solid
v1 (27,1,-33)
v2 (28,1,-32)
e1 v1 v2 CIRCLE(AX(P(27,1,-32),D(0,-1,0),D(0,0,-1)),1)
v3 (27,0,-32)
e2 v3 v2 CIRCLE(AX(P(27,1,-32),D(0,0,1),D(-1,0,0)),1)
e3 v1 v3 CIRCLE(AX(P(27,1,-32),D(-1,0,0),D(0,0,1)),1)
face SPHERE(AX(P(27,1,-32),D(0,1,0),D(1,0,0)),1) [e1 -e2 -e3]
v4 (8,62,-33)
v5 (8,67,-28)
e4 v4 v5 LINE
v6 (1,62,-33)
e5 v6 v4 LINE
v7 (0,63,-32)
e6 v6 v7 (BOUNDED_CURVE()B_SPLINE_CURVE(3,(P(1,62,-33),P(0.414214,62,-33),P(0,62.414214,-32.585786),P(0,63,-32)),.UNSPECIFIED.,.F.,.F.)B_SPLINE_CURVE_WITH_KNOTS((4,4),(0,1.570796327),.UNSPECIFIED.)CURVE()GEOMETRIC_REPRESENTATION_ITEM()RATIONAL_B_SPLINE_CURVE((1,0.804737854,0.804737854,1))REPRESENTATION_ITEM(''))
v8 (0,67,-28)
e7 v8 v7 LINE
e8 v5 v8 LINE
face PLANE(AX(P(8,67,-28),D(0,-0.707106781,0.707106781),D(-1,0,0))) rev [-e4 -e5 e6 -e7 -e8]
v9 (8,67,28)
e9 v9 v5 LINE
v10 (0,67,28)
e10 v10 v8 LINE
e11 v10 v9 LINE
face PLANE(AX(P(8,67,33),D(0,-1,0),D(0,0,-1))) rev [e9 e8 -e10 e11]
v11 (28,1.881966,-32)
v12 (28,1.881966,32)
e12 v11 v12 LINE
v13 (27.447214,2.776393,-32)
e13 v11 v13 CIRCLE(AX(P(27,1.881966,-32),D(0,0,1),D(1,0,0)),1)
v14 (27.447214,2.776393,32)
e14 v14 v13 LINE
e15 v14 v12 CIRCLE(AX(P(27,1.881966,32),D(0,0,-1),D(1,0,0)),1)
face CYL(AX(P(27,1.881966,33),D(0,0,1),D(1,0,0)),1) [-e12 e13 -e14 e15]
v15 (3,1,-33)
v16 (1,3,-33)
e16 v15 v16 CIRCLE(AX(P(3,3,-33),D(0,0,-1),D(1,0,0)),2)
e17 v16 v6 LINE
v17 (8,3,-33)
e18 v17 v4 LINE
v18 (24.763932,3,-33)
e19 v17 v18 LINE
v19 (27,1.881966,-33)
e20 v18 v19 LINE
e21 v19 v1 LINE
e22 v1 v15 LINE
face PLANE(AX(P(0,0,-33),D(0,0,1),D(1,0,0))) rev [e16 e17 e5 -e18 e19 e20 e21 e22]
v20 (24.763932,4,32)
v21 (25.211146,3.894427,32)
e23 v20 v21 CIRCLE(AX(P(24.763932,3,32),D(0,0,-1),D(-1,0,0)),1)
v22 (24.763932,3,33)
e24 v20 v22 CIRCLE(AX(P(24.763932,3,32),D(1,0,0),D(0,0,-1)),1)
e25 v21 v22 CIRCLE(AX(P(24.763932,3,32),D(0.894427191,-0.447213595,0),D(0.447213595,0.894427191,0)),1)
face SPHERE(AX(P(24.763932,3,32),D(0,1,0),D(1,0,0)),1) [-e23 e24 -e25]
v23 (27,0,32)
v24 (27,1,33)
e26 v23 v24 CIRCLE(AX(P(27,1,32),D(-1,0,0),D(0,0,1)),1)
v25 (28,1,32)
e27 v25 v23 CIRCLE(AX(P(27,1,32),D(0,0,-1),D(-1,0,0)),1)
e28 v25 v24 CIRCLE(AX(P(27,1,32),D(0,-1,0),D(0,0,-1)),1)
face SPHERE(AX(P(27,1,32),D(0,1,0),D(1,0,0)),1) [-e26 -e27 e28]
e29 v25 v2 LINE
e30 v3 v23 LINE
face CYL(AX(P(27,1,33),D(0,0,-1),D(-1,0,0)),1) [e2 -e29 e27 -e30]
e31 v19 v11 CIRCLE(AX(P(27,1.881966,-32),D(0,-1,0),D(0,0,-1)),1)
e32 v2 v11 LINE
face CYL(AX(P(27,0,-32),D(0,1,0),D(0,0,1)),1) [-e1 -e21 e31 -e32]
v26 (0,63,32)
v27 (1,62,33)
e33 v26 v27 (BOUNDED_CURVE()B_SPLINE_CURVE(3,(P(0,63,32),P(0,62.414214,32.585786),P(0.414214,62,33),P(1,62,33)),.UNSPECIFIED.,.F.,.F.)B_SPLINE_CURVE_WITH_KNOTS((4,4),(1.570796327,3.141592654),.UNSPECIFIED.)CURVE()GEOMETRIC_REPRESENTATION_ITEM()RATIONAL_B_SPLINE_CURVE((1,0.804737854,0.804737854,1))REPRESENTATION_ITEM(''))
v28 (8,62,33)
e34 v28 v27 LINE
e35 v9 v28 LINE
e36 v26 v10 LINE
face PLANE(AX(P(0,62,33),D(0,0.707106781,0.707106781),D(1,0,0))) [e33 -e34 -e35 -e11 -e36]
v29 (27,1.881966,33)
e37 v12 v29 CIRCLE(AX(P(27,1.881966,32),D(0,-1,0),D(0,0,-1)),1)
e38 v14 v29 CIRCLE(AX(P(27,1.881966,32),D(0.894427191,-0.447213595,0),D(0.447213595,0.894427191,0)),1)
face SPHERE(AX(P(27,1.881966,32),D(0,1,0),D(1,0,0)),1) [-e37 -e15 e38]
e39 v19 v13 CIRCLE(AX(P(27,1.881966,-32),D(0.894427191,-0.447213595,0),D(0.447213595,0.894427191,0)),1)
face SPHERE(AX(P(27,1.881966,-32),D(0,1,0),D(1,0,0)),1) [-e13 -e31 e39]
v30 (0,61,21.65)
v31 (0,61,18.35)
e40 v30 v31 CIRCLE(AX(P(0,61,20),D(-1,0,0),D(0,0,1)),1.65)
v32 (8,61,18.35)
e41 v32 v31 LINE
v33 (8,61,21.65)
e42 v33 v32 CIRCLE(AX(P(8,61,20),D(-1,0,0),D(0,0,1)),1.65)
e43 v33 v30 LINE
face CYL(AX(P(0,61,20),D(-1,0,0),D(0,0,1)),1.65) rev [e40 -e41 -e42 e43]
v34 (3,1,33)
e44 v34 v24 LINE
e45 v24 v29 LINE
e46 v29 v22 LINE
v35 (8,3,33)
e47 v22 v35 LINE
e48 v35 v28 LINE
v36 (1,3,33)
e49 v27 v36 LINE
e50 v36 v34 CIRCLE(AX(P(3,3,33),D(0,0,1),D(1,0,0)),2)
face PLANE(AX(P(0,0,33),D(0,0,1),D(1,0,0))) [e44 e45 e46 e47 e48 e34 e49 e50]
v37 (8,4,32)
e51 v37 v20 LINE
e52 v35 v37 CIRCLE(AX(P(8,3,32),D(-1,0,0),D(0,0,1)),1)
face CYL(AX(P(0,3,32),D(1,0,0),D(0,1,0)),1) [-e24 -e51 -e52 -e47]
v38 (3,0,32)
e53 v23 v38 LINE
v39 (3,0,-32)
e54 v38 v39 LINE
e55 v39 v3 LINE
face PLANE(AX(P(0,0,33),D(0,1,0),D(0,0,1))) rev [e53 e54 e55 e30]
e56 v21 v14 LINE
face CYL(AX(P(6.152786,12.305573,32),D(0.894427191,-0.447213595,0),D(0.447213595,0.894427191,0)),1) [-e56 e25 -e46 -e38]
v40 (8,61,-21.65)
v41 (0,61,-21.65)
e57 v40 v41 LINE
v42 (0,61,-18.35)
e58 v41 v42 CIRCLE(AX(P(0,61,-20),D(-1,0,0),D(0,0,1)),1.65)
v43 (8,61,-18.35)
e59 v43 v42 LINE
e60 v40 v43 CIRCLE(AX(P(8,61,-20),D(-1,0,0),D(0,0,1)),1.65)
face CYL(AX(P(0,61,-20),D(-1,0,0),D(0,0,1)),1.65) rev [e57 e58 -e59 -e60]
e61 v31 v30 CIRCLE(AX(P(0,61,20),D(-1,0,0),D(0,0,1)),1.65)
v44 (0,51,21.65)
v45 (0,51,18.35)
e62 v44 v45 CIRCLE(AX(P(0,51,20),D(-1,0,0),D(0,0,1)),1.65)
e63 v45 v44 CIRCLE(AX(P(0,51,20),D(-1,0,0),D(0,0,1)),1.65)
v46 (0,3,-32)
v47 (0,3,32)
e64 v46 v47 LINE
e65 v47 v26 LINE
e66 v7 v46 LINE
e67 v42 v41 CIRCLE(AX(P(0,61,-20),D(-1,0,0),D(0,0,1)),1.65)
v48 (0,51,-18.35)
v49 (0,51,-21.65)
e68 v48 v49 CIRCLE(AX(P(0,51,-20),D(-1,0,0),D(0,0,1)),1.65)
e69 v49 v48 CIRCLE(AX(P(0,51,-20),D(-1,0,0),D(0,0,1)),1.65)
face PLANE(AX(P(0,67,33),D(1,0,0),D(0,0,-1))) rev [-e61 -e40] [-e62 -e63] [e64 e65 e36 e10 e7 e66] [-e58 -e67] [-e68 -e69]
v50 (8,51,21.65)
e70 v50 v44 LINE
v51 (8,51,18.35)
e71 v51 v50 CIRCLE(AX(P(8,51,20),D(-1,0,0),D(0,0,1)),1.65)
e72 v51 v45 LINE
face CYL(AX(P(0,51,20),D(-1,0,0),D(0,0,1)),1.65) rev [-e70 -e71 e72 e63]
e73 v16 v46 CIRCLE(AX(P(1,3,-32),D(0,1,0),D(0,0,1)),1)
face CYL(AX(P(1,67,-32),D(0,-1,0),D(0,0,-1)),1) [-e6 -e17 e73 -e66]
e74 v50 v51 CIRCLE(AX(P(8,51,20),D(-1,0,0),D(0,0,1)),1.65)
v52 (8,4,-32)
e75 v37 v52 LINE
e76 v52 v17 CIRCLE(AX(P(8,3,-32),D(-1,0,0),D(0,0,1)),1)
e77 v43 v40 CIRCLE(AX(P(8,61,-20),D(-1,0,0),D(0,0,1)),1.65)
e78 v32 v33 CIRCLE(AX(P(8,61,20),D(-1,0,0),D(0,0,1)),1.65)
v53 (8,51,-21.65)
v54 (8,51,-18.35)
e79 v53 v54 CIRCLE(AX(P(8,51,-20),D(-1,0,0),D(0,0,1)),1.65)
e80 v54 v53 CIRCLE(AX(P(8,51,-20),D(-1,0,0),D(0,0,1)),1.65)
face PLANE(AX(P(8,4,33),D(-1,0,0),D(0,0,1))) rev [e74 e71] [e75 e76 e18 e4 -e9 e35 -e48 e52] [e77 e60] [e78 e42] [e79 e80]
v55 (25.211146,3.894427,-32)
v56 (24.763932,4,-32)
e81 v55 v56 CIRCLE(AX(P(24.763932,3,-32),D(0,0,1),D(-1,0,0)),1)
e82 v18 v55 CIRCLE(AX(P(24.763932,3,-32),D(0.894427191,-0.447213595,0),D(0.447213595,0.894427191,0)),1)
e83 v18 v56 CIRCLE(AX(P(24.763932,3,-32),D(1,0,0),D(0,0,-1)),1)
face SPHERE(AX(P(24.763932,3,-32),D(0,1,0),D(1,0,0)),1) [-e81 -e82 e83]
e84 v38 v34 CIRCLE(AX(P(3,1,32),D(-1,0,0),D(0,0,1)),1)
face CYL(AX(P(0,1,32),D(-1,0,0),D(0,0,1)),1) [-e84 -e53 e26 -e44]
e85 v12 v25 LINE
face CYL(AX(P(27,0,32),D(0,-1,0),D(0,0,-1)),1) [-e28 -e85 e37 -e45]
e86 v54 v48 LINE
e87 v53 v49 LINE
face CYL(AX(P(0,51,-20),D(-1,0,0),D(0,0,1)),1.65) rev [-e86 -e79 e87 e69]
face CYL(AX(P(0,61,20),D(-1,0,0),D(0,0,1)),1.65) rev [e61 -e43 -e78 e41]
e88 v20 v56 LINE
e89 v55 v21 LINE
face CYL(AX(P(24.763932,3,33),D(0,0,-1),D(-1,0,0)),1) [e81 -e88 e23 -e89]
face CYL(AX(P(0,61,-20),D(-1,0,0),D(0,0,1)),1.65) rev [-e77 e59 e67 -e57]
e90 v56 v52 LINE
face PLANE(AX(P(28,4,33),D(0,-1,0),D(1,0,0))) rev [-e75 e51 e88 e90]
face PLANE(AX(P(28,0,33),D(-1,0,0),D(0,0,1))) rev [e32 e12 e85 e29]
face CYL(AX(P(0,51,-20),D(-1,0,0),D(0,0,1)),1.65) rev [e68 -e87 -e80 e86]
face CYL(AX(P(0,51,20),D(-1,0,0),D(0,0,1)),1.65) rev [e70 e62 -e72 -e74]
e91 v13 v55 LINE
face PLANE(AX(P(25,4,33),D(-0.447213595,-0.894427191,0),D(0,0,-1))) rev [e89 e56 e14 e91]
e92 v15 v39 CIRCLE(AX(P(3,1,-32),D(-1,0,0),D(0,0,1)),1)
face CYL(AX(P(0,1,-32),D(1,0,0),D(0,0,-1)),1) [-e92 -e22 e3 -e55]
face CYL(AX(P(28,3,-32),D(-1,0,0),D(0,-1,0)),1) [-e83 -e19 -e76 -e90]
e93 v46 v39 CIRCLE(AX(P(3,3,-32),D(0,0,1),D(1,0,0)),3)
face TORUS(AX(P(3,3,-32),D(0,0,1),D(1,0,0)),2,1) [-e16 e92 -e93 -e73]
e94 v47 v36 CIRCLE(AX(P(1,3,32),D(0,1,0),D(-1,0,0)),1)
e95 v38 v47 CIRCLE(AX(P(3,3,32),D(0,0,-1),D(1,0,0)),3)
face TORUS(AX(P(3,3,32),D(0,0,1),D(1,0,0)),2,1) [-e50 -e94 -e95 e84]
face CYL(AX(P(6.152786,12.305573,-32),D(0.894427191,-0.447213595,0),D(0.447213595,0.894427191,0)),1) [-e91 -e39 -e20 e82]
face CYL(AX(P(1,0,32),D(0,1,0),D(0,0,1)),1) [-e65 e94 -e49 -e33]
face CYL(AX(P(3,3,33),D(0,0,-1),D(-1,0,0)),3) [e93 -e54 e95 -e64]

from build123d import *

# Parameters (mm, degrees)
EXTRUDE_1_DEPTH    = 33
CHAMFER_1_SIZE     = 1.5
CHAMFER_1_SIZE2    = 3
FILLET_1_R         = 1
CHAMFER_2_SIZE     = 5
FILLET_3_R         = 3
FILLET_4_R         = 1
HOLE_WIZARD_M4_2_D = 3.3


with BuildPart() as part:
    # 草图1 → 凸台-拉伸1 (new, symmetric)
    with BuildSketch(Plane.XY):
        Polygon((0, 67), (0, 0), (28, 0), (28, 4), (8, 4), (8, 67), align=None)
    extrude(amount=EXTRUDE_1_DEPTH, both=True)

    # 倒角1
    chamfer_1_edges = [part.edges().sort_by_distance(p)[0] for p in [
        (28, 4, 0),
    ]]
    chamfer_1_side = [part.faces().sort_by_distance(p)[0] for p in [
        (28, 2, 0),
    ]]
    chamfer(chamfer_1_edges, length=CHAMFER_1_SIZE, length2=CHAMFER_1_SIZE2, reference=chamfer_1_side[0])

    # 圆角1
    fillet_1_edges = [part.edges().sort_by_distance(p)[0] for p in [
        (28, 0, 0),
        (25, 4, 0),
        (28, 2.5, 0),
    ]]
    fillet(fillet_1_edges, radius=FILLET_1_R)

    # 倒角2
    chamfer_2_edges = [part.edges().sort_by_distance(p)[0] for p in [
        (4, 67, 33),
        (4, 67, -33),
    ]]
    chamfer(chamfer_2_edges, length=CHAMFER_2_SIZE)

    # 圆角3
    fillet_3_edges = [part.edges().sort_by_distance(p)[0] for p in [
        (0, 0, 0),
    ]]
    fillet(fillet_3_edges, radius=FILLET_3_R)

    # 圆角4
    fillet_4_edges = [part.edges().sort_by_distance(p)[0] for p in [
        (28, 1.440983006, -33),
        (28, 1.440983006, 33),
        (16.381966011, 4, -33),
        (26.329179607, 3.335410197, -33),
        (24.993684943, 3.973248989, -33),
        (27.850650808, 2.407697123, -33),
        (27.707106781, 0.292893219, -33),
        (26.329179607, 3.335410197, 33),
        (16.381966011, 4, 33),
        (24.993684943, 3.973248989, 33),
        (27.850650808, 2.407697123, 33),
        (27.707106781, 0.292893219, 33),
        (0, 32.5, 33),
        (0, 32.5, -33),
        (15, 0, -33),
        (15, 0, 33),
        (0.878679656, 0.878679656, -33),
        (0.878679656, 0.878679656, 33),
    ]]
    fillet(fillet_4_edges, radius=FILLET_4_R)

    # M4 螺纹孔2 (through all)
    with Locations(Plane.ZY):
        with Locations((-20, 61), (20, 61), (-20, 51), (20, 51)):
            Hole(HOLE_WIZARD_M4_2_D / 2)


solid = part.part
